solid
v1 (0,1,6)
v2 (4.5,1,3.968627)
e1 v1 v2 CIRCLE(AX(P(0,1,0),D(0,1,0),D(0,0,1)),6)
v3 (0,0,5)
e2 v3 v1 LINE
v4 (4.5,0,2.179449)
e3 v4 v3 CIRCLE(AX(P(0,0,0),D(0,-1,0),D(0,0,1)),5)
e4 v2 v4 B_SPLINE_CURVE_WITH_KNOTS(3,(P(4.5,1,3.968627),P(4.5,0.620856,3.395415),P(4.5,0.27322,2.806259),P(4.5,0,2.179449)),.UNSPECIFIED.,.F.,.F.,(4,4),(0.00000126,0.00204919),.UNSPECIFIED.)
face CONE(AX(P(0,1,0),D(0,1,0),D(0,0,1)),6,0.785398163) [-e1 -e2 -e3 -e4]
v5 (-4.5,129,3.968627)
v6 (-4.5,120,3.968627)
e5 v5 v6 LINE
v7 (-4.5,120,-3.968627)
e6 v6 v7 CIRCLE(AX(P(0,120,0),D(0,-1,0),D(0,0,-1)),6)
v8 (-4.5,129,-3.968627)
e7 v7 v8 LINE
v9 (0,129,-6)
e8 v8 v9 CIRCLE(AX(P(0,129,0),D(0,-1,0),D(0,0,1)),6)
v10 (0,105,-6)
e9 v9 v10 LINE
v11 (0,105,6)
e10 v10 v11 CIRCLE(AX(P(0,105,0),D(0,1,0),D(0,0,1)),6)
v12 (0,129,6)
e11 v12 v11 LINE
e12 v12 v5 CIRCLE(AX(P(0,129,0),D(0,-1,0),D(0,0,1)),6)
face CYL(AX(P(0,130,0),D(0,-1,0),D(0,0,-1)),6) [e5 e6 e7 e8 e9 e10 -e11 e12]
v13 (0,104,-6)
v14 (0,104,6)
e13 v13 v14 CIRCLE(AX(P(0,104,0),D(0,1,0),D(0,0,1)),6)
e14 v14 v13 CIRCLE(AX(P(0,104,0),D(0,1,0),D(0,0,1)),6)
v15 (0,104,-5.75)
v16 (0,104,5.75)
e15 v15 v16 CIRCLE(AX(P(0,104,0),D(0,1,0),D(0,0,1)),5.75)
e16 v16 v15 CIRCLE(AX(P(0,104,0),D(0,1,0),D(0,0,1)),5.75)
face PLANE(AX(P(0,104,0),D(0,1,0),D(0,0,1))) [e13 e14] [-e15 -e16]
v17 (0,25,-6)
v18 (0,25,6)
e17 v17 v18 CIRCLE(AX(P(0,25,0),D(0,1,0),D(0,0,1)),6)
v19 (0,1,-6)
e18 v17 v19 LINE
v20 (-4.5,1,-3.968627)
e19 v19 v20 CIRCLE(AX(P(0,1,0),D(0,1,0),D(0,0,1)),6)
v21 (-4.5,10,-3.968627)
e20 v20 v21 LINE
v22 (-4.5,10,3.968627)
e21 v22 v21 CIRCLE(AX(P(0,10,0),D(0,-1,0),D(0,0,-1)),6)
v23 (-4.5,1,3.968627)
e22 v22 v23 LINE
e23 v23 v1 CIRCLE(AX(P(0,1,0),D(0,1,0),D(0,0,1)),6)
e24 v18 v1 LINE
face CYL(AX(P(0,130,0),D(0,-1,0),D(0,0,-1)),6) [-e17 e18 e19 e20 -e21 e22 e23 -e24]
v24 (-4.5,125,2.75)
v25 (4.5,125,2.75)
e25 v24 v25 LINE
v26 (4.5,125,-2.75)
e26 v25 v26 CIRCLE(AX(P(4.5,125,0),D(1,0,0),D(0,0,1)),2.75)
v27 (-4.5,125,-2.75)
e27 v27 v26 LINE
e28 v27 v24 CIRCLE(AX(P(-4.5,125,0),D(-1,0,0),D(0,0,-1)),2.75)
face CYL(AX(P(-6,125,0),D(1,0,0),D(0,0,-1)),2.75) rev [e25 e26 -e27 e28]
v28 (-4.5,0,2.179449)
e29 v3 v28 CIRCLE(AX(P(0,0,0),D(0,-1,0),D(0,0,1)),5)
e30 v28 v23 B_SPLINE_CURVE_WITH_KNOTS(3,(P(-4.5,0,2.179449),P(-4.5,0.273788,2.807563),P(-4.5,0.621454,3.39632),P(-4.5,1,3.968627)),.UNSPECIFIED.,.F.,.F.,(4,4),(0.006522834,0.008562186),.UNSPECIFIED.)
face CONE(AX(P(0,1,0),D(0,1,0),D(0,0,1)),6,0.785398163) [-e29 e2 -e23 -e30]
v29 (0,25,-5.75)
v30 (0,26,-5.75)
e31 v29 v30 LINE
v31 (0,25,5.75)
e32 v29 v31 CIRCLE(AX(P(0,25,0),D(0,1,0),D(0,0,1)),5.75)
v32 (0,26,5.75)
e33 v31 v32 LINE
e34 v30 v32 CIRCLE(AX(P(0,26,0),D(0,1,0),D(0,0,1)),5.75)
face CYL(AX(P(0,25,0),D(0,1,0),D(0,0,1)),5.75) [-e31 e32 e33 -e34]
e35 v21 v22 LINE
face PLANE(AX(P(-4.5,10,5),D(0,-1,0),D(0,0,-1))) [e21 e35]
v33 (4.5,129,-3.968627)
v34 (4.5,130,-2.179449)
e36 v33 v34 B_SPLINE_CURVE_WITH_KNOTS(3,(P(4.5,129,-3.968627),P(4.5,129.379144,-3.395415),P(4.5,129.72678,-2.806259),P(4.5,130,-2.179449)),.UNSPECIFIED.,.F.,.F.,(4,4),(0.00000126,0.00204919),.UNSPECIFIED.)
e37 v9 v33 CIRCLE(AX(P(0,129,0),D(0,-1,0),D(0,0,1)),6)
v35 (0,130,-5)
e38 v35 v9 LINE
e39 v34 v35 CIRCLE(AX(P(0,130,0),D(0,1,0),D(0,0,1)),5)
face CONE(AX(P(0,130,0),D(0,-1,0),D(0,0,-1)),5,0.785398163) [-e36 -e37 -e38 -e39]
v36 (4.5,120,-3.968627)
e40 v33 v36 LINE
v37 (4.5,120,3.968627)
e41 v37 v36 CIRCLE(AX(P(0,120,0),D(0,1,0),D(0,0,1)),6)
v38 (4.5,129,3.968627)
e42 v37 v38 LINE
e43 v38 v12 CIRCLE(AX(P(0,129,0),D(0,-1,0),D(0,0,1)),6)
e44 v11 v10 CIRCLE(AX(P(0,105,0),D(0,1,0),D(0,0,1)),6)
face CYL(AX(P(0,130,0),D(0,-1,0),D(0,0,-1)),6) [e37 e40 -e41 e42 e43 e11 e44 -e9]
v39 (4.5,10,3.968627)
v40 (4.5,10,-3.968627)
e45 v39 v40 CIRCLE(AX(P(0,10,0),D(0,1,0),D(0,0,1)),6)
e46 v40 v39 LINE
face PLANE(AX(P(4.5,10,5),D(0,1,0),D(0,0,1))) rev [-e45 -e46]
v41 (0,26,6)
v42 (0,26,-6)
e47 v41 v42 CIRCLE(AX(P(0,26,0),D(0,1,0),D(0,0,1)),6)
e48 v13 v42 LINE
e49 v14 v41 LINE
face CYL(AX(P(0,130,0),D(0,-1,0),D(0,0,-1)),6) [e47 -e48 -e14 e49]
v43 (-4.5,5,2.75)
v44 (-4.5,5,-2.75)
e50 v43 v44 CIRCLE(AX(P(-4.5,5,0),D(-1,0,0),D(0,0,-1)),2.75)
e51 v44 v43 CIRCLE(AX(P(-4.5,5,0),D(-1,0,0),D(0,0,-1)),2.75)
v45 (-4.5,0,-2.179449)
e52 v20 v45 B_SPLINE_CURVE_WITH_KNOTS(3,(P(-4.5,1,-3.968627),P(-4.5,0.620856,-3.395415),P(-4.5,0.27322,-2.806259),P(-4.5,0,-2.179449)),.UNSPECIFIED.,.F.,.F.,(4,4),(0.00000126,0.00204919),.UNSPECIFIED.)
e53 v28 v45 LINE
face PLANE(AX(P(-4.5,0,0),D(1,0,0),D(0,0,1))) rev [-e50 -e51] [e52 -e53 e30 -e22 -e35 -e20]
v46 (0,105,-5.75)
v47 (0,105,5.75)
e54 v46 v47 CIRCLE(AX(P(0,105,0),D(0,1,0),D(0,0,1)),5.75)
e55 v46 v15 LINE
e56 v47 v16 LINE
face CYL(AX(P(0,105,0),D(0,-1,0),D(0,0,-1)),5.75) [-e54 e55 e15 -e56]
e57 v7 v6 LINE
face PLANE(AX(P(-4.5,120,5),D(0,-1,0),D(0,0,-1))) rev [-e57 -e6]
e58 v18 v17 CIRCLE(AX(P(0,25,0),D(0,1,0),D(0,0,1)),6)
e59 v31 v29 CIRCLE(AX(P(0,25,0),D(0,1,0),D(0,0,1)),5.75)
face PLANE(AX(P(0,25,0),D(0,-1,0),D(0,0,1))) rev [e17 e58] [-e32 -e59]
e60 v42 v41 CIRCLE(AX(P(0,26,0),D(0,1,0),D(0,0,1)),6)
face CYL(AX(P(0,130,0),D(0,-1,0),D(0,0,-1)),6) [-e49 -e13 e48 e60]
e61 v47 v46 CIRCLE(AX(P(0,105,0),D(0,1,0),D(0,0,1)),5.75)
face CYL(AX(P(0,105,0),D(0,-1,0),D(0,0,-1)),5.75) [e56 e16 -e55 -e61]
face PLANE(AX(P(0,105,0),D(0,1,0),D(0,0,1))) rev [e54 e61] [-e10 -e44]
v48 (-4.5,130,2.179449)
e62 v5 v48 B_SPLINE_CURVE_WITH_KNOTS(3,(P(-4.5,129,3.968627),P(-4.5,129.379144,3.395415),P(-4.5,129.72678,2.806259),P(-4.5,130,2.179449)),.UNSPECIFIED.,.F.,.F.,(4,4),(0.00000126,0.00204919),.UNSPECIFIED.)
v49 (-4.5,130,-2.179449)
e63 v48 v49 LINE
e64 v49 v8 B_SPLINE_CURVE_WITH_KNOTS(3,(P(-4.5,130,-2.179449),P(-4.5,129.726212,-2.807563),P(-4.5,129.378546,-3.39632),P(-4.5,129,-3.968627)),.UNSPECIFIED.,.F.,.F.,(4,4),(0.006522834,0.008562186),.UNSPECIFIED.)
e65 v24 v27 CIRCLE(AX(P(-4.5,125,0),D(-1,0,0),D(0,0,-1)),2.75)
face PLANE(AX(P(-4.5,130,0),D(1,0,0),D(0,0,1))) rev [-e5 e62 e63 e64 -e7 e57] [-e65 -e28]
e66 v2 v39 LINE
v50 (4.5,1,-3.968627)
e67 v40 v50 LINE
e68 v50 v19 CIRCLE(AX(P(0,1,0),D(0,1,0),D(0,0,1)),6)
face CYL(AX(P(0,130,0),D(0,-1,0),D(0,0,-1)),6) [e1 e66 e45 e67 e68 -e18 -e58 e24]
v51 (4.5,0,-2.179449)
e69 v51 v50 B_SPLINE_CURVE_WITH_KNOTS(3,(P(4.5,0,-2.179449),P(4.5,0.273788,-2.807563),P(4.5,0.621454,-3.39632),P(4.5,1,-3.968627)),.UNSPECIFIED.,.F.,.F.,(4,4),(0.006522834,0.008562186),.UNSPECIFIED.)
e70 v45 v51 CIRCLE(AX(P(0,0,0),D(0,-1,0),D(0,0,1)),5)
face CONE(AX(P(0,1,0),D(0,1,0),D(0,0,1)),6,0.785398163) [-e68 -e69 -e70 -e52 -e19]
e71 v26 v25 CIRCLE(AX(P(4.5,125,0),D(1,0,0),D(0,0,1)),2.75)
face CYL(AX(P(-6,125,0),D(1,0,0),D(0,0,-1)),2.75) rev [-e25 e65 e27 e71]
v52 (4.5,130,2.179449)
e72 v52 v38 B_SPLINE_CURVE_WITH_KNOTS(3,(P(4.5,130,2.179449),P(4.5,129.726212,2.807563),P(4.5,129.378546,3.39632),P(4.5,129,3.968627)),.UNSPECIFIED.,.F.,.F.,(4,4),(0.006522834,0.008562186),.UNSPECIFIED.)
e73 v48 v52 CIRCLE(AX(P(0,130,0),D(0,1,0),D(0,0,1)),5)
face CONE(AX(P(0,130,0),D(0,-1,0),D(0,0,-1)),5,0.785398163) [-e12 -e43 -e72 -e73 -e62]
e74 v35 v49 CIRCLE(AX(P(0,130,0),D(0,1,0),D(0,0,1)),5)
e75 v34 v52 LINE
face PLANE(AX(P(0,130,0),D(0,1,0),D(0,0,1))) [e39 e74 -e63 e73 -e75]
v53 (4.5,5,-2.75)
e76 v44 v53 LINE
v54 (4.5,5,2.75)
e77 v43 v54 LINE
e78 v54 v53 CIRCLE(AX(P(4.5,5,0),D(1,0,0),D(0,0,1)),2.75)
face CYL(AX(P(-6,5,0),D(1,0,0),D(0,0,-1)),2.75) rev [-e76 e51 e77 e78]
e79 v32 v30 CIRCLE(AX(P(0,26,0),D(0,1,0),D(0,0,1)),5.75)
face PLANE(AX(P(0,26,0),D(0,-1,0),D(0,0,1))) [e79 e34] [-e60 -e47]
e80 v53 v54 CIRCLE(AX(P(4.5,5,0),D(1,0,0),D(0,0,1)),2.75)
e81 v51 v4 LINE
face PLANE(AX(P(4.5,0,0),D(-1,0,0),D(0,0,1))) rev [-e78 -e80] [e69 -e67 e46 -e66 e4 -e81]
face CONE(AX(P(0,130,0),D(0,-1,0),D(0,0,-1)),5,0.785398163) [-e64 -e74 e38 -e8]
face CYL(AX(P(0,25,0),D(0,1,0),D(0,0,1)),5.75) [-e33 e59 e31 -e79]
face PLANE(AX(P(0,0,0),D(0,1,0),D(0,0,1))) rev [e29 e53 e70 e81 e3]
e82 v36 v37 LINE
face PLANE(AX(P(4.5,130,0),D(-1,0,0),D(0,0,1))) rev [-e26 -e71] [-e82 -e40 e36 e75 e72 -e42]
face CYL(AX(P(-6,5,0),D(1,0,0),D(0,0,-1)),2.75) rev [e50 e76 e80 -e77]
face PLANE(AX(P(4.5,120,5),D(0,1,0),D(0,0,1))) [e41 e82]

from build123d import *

# Parameters (mm, degrees)
SKETCH1_R               = 6
BOSS_EXTRUDE1_DEPTH     = 130
CUT_EXTRUDE1_DEPTH      = 131.276628756
CUT_EXTRUDE1_DEPTH_BACK = 131.276628756
SKETCH3_R               = 2.75
CHAMFER1_SIZE           = 1
SKETCH5_W               = 10
SKETCH5_H               = 20
CUT_EXTRUDE2_DEPTH      = 1.5
MIRROR2_COPY_1_SKETCH_W = 10
MIRROR2_COPY_1_SKETCH_H = 20
MIRROR2_COPY_1_DEPTH    = 1.5
SKETCH7_R               = 6
SKETCH7_R_2             = 5.75
CUT_EXTRUDE3_DEPTH      = 1


with BuildPart() as part:
    # Sketch1 → Boss-Extrude1 (new body)
    with BuildSketch(Plane(origin=(0, 0, 0), x_dir=(1, 0, 0), z_dir=(0, 1, 0))):
        with Locations(Location((0, 0, 0), (0, 0, 270))):
            Circle(SKETCH1_R)
    extrude(amount=BOSS_EXTRUDE1_DEPTH)

    # Sketch3 → Cut-Extrude1 (cut, two sides: drawn at the far end of the back side and taken through both)
    with BuildSketch(Plane(origin=(0, 0, 0), x_dir=(0, 0, -1), z_dir=(1, 0, 0)).offset(-CUT_EXTRUDE1_DEPTH_BACK)):
        with Locations((0, 125)):
            Circle(SKETCH3_R)
        with Locations((0, 5)):
            Circle(SKETCH3_R)
    extrude(amount=CUT_EXTRUDE1_DEPTH + CUT_EXTRUDE1_DEPTH_BACK, mode=Mode.SUBTRACT)

    # Chamfer1
    chamfer1_edges = [part.edges().sort_by_distance(p)[0] for p in [
        (0, 0, -6),
        (0, 130, -6),
    ]]
    chamfer(chamfer1_edges, length=CHAMFER1_SIZE)

    # Sketch5 → Cut-Extrude2 (cut)
    with BuildSketch(Plane(origin=(6, 0, 0), x_dir=(0, 0, -1), z_dir=(1, 0, 0))):
        Rectangle(SKETCH5_W, SKETCH5_H)
    cut_extrude2 = extrude(amount=-CUT_EXTRUDE2_DEPTH, mode=Mode.SUBTRACT)

    # Mirror1: Cut-Extrude2 across plane
    add(cut_extrude2.mirror(Plane(origin=(0, 0, 0), x_dir=(0, 0, 1), z_dir=(1, 0, 0))), mode=Mode.SUBTRACT)

    # Mirror2: Cut-Extrude2 across plane
    add(cut_extrude2.mirror(Plane(origin=(0, 65, 0), x_dir=(0, 0, 1), z_dir=(0, -1, 0))), mode=Mode.SUBTRACT)

    # Mirror2 copy 1 sketch → Mirror2 copy 1 (cut)
    with BuildSketch(Plane(origin=(-6, 130, 0), x_dir=(0, 0, -1), z_dir=(-1, 0, 0))):
        Rectangle(MIRROR2_COPY_1_SKETCH_W, MIRROR2_COPY_1_SKETCH_H)
    extrude(amount=-MIRROR2_COPY_1_DEPTH, mode=Mode.SUBTRACT)

    # Sketch7 → Cut-Extrude3 (cut)
    with BuildSketch(Plane(origin=(0, 104, 0), x_dir=(1, 0, 0), z_dir=(0, 1, 0))):
        with Locations(Location((0, 0, 0), (0, 0, 138.590377891))):
            Circle(SKETCH7_R)
        with Locations(Location((0, 0, 0), (0, 0, 270))):
            Circle(SKETCH7_R_2, mode=Mode.SUBTRACT)
    cut_extrude3 = extrude(amount=CUT_EXTRUDE3_DEPTH, mode=Mode.SUBTRACT)

    # Mirror3: Cut-Extrude3 across plane
    add(cut_extrude3.mirror(Plane(origin=(0, 65, 0), x_dir=(0, 0, 1), z_dir=(0, -1, 0))), mode=Mode.SUBTRACT)


solid = part.part
